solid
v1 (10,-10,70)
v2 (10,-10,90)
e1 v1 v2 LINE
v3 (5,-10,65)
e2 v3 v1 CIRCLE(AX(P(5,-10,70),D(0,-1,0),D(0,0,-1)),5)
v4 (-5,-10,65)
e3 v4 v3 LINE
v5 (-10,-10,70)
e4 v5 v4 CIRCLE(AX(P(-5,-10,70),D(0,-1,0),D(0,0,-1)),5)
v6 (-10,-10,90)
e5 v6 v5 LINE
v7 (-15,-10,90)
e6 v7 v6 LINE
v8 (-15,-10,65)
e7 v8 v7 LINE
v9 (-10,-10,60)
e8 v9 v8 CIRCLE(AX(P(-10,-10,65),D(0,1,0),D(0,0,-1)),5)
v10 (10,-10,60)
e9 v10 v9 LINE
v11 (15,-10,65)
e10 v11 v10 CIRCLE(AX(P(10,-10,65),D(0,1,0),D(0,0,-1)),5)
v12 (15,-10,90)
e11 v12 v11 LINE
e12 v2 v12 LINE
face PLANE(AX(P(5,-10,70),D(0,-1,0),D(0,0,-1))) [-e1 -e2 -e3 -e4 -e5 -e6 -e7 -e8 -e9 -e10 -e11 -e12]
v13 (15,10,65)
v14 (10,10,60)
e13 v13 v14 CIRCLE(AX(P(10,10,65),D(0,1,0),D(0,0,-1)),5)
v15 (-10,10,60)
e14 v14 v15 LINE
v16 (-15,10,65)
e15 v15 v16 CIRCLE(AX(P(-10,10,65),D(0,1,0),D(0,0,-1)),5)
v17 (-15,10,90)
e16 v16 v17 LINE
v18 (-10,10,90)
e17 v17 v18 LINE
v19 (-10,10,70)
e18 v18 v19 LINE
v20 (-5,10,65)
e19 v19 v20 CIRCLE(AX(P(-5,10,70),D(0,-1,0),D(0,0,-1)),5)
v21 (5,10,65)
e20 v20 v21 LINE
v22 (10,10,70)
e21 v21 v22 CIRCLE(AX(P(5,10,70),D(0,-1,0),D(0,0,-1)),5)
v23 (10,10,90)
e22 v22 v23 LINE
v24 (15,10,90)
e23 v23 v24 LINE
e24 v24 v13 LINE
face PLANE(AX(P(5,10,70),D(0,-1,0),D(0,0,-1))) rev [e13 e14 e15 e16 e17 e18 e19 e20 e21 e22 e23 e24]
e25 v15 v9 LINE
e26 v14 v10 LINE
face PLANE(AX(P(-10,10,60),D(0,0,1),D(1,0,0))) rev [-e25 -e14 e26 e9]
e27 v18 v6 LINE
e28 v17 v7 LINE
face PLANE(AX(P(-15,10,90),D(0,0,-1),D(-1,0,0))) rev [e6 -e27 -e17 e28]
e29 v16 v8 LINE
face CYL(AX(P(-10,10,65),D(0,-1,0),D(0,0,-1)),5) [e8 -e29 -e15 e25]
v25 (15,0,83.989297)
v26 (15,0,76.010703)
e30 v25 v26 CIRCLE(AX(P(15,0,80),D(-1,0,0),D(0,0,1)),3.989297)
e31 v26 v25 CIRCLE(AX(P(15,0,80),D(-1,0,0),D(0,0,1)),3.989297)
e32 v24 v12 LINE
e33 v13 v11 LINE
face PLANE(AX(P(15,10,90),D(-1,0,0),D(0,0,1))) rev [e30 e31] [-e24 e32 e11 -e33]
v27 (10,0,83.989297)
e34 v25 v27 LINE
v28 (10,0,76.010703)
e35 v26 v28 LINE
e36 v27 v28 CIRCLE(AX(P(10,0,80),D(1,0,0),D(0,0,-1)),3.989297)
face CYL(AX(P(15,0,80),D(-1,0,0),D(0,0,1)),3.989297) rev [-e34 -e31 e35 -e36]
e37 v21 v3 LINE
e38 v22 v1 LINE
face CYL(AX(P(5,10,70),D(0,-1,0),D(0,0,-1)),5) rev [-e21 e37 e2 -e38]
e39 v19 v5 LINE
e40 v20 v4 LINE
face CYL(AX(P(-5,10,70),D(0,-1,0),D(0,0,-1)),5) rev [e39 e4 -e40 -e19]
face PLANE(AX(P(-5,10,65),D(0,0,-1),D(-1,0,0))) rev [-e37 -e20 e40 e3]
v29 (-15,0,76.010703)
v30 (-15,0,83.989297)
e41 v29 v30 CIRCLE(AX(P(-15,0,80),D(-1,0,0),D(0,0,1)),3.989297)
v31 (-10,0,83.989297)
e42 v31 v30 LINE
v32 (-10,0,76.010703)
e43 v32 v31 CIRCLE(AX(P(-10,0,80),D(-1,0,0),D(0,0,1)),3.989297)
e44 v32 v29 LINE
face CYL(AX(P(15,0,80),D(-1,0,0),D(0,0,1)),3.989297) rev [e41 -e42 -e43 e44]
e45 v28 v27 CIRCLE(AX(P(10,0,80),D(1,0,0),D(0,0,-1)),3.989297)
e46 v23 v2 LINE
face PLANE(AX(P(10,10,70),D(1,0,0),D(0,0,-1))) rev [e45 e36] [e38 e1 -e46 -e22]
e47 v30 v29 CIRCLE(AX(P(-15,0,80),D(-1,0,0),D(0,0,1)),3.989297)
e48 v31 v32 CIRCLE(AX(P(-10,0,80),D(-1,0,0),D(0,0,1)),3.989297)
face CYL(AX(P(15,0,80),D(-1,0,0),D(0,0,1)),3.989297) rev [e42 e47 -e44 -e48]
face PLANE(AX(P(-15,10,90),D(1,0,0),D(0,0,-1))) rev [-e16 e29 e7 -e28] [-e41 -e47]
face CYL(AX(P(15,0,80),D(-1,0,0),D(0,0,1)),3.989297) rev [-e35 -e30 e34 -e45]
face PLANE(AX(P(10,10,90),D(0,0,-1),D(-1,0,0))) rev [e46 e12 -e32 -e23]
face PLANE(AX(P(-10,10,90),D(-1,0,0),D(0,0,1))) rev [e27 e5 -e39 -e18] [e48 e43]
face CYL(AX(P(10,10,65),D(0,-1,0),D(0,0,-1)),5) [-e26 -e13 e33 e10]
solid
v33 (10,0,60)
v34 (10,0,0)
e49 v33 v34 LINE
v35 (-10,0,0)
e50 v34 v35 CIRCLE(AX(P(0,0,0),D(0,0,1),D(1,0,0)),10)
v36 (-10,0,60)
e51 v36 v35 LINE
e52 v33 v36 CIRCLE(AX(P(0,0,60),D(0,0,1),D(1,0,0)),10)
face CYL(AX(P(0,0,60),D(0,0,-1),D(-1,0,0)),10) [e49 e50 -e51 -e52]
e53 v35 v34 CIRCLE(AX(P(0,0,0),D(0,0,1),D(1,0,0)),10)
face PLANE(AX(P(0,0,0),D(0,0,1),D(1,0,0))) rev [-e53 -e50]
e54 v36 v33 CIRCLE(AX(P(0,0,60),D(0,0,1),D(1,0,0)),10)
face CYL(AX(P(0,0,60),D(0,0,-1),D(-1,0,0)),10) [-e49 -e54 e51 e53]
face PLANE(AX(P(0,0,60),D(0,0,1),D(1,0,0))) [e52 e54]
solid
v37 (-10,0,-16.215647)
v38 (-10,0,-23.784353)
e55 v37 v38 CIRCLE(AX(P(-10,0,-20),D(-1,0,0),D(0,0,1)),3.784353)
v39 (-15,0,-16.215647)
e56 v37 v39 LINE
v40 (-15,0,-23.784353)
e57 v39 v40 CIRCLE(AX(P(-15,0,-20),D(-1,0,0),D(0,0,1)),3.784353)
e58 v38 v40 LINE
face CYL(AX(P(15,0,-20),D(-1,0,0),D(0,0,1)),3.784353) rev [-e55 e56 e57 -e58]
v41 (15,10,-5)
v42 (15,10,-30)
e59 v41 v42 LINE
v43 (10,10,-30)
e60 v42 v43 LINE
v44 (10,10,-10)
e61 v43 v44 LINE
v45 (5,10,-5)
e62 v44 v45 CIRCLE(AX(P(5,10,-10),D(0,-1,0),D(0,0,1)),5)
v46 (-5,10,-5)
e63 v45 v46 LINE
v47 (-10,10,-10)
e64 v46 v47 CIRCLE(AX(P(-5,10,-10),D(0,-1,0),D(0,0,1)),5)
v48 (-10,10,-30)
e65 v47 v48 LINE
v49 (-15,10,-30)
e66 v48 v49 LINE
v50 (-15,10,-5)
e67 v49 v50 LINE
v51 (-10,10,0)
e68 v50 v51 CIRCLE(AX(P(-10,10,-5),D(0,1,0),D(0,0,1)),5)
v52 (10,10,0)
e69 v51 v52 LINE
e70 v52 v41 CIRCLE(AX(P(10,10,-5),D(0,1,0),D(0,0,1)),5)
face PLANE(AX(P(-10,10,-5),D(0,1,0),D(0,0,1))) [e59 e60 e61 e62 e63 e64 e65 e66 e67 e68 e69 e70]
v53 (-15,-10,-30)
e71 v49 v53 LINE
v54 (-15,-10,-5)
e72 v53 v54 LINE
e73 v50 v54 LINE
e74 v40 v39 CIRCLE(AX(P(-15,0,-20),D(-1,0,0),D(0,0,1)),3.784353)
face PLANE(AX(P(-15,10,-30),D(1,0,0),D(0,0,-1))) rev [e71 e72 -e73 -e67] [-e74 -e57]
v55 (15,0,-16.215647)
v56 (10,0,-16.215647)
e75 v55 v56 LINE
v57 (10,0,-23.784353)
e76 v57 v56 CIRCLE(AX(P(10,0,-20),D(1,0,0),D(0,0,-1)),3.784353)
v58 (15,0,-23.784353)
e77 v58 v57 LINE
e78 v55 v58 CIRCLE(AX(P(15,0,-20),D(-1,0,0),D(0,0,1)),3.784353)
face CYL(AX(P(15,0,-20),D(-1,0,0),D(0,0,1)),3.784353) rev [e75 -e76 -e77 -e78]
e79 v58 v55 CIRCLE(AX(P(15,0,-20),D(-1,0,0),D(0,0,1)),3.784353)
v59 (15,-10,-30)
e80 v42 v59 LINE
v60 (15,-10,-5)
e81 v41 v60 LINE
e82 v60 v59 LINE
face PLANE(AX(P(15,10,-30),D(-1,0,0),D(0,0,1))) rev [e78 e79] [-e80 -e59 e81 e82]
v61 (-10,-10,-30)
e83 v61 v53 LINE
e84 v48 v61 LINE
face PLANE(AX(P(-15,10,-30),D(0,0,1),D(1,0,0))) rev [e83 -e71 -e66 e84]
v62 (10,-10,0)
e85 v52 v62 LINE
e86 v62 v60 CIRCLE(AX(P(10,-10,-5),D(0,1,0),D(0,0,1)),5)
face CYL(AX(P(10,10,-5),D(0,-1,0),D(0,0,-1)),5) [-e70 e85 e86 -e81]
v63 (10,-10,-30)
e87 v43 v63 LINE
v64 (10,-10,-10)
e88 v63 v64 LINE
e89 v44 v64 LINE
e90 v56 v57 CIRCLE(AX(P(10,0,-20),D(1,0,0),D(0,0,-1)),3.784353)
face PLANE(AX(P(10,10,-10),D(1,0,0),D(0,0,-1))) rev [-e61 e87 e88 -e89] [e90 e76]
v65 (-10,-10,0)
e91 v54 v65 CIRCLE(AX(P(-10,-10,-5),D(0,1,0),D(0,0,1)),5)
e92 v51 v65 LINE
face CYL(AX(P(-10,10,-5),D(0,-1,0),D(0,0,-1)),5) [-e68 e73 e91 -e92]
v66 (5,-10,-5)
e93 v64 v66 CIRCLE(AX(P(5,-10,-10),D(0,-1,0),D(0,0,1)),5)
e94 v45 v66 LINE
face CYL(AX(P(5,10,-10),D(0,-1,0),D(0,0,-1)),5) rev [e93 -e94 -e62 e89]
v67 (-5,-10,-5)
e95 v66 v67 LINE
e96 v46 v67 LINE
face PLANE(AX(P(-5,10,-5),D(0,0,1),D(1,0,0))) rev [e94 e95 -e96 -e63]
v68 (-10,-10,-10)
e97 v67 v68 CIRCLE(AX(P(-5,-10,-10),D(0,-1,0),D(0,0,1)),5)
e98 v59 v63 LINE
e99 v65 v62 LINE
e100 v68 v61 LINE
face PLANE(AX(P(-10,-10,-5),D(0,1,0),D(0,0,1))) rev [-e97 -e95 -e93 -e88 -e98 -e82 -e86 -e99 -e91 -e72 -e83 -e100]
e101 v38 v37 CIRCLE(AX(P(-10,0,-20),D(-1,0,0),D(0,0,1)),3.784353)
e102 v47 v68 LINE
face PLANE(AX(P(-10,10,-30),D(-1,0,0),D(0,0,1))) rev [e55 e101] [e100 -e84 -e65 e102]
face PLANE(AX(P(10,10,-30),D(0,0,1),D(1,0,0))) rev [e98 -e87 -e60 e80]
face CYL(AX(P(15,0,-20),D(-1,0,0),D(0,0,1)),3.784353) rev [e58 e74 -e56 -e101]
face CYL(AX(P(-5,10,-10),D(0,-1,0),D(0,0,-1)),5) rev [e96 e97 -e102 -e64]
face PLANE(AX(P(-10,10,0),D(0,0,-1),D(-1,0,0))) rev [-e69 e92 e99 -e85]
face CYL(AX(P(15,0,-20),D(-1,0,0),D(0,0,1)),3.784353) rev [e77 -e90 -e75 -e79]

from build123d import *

# Parameters (mm, degrees)
SKETCH1_R             = 10
BOSS_EXTRUDE1_DEPTH   = 60
BOSS_EXTRUDE2_DEPTH   = 10
BOSS_EXTRUDE2_2_DEPTH = 10
SKETCH3_R             = 3.989297241
SKETCH3_R_2           = 3.784352929
CUT_EXTRUDE1_DEPTH    = 96.393920142


with BuildPart() as part:
    # Sketch1 → Boss-Extrude1 (new body)
    with BuildSketch(Plane.XY):
        Circle(SKETCH1_R)
    extrude(amount=BOSS_EXTRUDE1_DEPTH)


with BuildPart() as body_2:
    # Sketch2 → Boss-Extrude2 (new, symmetric)
    with BuildSketch(Plane(origin=(0, 0, 0), x_dir=(1, 0, 0), z_dir=(0, 1, 0))):
        with BuildLine():
            Line((-15, 30), (-10, 30))
            Line((-10, 30), (-10, 10))
            ThreePointArc((-10, 10), (-8.535533906, 6.464466094), (-5, 5))
            Line((-5, 5), (5, 5))
            ThreePointArc((5, 5), (8.535533906, 6.464466094), (10, 10))
            Line((10, 10), (10, 30))
            Line((10, 30), (15, 30))
            Line((15, 30), (15, 5))
            ThreePointArc((15, 5), (13.535533906, 1.464466094), (10, 0))
            Line((10, 0), (-10, 0))
            ThreePointArc((-10, 0), (-13.535533906, 1.464466094), (-15, 5))
            Line((-15, 5), (-15, 30))
        make_face()
    extrude(amount=BOSS_EXTRUDE2_DEPTH, both=True)


with BuildPart() as body_3:
    # Sketch2 → Boss-Extrude2 2 (new, symmetric)
    with BuildSketch(Plane(origin=(0, 0, 0), x_dir=(1, 0, 0), z_dir=(0, 1, 0))):
        with BuildLine():
            Line((10, -90), (15, -90))
            Line((15, -90), (15, -65))
            ThreePointArc((15, -65), (13.535533906, -61.464466094), (10, -60))
            Line((10, -60), (-10, -60))
            ThreePointArc((-10, -60), (-13.535533906, -61.464466094), (-15, -65))
            Line((-15, -65), (-15, -90))
            Line((-15, -90), (-10, -90))
            Line((-10, -90), (-10, -70))
            ThreePointArc((-10, -70), (-8.535533906, -66.464466094), (-5, -65))
            Line((-5, -65), (5, -65))
            ThreePointArc((5, -65), (8.535533906, -66.464466094), (10, -70))
            Line((10, -70), (10, -90))
        make_face()
    extrude(amount=BOSS_EXTRUDE2_2_DEPTH, both=True)


with BuildPart() as cut_extrude1_tool:
    # Sketch3 → Cut-Extrude1 (new, through all)
    with BuildSketch(Plane.ZY.offset(15)):
        with Locations((80, 0)):
            Circle(SKETCH3_R)
        with Locations((-20, 0)):
            Circle(SKETCH3_R_2)
    extrude(amount=-CUT_EXTRUDE1_DEPTH)


with BuildPart() as body_2_1:
    add(body_2.part)

    # Cut-Extrude1: cut by cut_extrude1_tool
    add(cut_extrude1_tool.part, mode=Mode.SUBTRACT)


with BuildPart() as body_3_1:
    add(body_3.part)

    # Cut-Extrude1: cut by cut_extrude1_tool
    add(cut_extrude1_tool.part, mode=Mode.SUBTRACT)


solid = Compound([part.part, body_2_1.part, body_3_1.part])
